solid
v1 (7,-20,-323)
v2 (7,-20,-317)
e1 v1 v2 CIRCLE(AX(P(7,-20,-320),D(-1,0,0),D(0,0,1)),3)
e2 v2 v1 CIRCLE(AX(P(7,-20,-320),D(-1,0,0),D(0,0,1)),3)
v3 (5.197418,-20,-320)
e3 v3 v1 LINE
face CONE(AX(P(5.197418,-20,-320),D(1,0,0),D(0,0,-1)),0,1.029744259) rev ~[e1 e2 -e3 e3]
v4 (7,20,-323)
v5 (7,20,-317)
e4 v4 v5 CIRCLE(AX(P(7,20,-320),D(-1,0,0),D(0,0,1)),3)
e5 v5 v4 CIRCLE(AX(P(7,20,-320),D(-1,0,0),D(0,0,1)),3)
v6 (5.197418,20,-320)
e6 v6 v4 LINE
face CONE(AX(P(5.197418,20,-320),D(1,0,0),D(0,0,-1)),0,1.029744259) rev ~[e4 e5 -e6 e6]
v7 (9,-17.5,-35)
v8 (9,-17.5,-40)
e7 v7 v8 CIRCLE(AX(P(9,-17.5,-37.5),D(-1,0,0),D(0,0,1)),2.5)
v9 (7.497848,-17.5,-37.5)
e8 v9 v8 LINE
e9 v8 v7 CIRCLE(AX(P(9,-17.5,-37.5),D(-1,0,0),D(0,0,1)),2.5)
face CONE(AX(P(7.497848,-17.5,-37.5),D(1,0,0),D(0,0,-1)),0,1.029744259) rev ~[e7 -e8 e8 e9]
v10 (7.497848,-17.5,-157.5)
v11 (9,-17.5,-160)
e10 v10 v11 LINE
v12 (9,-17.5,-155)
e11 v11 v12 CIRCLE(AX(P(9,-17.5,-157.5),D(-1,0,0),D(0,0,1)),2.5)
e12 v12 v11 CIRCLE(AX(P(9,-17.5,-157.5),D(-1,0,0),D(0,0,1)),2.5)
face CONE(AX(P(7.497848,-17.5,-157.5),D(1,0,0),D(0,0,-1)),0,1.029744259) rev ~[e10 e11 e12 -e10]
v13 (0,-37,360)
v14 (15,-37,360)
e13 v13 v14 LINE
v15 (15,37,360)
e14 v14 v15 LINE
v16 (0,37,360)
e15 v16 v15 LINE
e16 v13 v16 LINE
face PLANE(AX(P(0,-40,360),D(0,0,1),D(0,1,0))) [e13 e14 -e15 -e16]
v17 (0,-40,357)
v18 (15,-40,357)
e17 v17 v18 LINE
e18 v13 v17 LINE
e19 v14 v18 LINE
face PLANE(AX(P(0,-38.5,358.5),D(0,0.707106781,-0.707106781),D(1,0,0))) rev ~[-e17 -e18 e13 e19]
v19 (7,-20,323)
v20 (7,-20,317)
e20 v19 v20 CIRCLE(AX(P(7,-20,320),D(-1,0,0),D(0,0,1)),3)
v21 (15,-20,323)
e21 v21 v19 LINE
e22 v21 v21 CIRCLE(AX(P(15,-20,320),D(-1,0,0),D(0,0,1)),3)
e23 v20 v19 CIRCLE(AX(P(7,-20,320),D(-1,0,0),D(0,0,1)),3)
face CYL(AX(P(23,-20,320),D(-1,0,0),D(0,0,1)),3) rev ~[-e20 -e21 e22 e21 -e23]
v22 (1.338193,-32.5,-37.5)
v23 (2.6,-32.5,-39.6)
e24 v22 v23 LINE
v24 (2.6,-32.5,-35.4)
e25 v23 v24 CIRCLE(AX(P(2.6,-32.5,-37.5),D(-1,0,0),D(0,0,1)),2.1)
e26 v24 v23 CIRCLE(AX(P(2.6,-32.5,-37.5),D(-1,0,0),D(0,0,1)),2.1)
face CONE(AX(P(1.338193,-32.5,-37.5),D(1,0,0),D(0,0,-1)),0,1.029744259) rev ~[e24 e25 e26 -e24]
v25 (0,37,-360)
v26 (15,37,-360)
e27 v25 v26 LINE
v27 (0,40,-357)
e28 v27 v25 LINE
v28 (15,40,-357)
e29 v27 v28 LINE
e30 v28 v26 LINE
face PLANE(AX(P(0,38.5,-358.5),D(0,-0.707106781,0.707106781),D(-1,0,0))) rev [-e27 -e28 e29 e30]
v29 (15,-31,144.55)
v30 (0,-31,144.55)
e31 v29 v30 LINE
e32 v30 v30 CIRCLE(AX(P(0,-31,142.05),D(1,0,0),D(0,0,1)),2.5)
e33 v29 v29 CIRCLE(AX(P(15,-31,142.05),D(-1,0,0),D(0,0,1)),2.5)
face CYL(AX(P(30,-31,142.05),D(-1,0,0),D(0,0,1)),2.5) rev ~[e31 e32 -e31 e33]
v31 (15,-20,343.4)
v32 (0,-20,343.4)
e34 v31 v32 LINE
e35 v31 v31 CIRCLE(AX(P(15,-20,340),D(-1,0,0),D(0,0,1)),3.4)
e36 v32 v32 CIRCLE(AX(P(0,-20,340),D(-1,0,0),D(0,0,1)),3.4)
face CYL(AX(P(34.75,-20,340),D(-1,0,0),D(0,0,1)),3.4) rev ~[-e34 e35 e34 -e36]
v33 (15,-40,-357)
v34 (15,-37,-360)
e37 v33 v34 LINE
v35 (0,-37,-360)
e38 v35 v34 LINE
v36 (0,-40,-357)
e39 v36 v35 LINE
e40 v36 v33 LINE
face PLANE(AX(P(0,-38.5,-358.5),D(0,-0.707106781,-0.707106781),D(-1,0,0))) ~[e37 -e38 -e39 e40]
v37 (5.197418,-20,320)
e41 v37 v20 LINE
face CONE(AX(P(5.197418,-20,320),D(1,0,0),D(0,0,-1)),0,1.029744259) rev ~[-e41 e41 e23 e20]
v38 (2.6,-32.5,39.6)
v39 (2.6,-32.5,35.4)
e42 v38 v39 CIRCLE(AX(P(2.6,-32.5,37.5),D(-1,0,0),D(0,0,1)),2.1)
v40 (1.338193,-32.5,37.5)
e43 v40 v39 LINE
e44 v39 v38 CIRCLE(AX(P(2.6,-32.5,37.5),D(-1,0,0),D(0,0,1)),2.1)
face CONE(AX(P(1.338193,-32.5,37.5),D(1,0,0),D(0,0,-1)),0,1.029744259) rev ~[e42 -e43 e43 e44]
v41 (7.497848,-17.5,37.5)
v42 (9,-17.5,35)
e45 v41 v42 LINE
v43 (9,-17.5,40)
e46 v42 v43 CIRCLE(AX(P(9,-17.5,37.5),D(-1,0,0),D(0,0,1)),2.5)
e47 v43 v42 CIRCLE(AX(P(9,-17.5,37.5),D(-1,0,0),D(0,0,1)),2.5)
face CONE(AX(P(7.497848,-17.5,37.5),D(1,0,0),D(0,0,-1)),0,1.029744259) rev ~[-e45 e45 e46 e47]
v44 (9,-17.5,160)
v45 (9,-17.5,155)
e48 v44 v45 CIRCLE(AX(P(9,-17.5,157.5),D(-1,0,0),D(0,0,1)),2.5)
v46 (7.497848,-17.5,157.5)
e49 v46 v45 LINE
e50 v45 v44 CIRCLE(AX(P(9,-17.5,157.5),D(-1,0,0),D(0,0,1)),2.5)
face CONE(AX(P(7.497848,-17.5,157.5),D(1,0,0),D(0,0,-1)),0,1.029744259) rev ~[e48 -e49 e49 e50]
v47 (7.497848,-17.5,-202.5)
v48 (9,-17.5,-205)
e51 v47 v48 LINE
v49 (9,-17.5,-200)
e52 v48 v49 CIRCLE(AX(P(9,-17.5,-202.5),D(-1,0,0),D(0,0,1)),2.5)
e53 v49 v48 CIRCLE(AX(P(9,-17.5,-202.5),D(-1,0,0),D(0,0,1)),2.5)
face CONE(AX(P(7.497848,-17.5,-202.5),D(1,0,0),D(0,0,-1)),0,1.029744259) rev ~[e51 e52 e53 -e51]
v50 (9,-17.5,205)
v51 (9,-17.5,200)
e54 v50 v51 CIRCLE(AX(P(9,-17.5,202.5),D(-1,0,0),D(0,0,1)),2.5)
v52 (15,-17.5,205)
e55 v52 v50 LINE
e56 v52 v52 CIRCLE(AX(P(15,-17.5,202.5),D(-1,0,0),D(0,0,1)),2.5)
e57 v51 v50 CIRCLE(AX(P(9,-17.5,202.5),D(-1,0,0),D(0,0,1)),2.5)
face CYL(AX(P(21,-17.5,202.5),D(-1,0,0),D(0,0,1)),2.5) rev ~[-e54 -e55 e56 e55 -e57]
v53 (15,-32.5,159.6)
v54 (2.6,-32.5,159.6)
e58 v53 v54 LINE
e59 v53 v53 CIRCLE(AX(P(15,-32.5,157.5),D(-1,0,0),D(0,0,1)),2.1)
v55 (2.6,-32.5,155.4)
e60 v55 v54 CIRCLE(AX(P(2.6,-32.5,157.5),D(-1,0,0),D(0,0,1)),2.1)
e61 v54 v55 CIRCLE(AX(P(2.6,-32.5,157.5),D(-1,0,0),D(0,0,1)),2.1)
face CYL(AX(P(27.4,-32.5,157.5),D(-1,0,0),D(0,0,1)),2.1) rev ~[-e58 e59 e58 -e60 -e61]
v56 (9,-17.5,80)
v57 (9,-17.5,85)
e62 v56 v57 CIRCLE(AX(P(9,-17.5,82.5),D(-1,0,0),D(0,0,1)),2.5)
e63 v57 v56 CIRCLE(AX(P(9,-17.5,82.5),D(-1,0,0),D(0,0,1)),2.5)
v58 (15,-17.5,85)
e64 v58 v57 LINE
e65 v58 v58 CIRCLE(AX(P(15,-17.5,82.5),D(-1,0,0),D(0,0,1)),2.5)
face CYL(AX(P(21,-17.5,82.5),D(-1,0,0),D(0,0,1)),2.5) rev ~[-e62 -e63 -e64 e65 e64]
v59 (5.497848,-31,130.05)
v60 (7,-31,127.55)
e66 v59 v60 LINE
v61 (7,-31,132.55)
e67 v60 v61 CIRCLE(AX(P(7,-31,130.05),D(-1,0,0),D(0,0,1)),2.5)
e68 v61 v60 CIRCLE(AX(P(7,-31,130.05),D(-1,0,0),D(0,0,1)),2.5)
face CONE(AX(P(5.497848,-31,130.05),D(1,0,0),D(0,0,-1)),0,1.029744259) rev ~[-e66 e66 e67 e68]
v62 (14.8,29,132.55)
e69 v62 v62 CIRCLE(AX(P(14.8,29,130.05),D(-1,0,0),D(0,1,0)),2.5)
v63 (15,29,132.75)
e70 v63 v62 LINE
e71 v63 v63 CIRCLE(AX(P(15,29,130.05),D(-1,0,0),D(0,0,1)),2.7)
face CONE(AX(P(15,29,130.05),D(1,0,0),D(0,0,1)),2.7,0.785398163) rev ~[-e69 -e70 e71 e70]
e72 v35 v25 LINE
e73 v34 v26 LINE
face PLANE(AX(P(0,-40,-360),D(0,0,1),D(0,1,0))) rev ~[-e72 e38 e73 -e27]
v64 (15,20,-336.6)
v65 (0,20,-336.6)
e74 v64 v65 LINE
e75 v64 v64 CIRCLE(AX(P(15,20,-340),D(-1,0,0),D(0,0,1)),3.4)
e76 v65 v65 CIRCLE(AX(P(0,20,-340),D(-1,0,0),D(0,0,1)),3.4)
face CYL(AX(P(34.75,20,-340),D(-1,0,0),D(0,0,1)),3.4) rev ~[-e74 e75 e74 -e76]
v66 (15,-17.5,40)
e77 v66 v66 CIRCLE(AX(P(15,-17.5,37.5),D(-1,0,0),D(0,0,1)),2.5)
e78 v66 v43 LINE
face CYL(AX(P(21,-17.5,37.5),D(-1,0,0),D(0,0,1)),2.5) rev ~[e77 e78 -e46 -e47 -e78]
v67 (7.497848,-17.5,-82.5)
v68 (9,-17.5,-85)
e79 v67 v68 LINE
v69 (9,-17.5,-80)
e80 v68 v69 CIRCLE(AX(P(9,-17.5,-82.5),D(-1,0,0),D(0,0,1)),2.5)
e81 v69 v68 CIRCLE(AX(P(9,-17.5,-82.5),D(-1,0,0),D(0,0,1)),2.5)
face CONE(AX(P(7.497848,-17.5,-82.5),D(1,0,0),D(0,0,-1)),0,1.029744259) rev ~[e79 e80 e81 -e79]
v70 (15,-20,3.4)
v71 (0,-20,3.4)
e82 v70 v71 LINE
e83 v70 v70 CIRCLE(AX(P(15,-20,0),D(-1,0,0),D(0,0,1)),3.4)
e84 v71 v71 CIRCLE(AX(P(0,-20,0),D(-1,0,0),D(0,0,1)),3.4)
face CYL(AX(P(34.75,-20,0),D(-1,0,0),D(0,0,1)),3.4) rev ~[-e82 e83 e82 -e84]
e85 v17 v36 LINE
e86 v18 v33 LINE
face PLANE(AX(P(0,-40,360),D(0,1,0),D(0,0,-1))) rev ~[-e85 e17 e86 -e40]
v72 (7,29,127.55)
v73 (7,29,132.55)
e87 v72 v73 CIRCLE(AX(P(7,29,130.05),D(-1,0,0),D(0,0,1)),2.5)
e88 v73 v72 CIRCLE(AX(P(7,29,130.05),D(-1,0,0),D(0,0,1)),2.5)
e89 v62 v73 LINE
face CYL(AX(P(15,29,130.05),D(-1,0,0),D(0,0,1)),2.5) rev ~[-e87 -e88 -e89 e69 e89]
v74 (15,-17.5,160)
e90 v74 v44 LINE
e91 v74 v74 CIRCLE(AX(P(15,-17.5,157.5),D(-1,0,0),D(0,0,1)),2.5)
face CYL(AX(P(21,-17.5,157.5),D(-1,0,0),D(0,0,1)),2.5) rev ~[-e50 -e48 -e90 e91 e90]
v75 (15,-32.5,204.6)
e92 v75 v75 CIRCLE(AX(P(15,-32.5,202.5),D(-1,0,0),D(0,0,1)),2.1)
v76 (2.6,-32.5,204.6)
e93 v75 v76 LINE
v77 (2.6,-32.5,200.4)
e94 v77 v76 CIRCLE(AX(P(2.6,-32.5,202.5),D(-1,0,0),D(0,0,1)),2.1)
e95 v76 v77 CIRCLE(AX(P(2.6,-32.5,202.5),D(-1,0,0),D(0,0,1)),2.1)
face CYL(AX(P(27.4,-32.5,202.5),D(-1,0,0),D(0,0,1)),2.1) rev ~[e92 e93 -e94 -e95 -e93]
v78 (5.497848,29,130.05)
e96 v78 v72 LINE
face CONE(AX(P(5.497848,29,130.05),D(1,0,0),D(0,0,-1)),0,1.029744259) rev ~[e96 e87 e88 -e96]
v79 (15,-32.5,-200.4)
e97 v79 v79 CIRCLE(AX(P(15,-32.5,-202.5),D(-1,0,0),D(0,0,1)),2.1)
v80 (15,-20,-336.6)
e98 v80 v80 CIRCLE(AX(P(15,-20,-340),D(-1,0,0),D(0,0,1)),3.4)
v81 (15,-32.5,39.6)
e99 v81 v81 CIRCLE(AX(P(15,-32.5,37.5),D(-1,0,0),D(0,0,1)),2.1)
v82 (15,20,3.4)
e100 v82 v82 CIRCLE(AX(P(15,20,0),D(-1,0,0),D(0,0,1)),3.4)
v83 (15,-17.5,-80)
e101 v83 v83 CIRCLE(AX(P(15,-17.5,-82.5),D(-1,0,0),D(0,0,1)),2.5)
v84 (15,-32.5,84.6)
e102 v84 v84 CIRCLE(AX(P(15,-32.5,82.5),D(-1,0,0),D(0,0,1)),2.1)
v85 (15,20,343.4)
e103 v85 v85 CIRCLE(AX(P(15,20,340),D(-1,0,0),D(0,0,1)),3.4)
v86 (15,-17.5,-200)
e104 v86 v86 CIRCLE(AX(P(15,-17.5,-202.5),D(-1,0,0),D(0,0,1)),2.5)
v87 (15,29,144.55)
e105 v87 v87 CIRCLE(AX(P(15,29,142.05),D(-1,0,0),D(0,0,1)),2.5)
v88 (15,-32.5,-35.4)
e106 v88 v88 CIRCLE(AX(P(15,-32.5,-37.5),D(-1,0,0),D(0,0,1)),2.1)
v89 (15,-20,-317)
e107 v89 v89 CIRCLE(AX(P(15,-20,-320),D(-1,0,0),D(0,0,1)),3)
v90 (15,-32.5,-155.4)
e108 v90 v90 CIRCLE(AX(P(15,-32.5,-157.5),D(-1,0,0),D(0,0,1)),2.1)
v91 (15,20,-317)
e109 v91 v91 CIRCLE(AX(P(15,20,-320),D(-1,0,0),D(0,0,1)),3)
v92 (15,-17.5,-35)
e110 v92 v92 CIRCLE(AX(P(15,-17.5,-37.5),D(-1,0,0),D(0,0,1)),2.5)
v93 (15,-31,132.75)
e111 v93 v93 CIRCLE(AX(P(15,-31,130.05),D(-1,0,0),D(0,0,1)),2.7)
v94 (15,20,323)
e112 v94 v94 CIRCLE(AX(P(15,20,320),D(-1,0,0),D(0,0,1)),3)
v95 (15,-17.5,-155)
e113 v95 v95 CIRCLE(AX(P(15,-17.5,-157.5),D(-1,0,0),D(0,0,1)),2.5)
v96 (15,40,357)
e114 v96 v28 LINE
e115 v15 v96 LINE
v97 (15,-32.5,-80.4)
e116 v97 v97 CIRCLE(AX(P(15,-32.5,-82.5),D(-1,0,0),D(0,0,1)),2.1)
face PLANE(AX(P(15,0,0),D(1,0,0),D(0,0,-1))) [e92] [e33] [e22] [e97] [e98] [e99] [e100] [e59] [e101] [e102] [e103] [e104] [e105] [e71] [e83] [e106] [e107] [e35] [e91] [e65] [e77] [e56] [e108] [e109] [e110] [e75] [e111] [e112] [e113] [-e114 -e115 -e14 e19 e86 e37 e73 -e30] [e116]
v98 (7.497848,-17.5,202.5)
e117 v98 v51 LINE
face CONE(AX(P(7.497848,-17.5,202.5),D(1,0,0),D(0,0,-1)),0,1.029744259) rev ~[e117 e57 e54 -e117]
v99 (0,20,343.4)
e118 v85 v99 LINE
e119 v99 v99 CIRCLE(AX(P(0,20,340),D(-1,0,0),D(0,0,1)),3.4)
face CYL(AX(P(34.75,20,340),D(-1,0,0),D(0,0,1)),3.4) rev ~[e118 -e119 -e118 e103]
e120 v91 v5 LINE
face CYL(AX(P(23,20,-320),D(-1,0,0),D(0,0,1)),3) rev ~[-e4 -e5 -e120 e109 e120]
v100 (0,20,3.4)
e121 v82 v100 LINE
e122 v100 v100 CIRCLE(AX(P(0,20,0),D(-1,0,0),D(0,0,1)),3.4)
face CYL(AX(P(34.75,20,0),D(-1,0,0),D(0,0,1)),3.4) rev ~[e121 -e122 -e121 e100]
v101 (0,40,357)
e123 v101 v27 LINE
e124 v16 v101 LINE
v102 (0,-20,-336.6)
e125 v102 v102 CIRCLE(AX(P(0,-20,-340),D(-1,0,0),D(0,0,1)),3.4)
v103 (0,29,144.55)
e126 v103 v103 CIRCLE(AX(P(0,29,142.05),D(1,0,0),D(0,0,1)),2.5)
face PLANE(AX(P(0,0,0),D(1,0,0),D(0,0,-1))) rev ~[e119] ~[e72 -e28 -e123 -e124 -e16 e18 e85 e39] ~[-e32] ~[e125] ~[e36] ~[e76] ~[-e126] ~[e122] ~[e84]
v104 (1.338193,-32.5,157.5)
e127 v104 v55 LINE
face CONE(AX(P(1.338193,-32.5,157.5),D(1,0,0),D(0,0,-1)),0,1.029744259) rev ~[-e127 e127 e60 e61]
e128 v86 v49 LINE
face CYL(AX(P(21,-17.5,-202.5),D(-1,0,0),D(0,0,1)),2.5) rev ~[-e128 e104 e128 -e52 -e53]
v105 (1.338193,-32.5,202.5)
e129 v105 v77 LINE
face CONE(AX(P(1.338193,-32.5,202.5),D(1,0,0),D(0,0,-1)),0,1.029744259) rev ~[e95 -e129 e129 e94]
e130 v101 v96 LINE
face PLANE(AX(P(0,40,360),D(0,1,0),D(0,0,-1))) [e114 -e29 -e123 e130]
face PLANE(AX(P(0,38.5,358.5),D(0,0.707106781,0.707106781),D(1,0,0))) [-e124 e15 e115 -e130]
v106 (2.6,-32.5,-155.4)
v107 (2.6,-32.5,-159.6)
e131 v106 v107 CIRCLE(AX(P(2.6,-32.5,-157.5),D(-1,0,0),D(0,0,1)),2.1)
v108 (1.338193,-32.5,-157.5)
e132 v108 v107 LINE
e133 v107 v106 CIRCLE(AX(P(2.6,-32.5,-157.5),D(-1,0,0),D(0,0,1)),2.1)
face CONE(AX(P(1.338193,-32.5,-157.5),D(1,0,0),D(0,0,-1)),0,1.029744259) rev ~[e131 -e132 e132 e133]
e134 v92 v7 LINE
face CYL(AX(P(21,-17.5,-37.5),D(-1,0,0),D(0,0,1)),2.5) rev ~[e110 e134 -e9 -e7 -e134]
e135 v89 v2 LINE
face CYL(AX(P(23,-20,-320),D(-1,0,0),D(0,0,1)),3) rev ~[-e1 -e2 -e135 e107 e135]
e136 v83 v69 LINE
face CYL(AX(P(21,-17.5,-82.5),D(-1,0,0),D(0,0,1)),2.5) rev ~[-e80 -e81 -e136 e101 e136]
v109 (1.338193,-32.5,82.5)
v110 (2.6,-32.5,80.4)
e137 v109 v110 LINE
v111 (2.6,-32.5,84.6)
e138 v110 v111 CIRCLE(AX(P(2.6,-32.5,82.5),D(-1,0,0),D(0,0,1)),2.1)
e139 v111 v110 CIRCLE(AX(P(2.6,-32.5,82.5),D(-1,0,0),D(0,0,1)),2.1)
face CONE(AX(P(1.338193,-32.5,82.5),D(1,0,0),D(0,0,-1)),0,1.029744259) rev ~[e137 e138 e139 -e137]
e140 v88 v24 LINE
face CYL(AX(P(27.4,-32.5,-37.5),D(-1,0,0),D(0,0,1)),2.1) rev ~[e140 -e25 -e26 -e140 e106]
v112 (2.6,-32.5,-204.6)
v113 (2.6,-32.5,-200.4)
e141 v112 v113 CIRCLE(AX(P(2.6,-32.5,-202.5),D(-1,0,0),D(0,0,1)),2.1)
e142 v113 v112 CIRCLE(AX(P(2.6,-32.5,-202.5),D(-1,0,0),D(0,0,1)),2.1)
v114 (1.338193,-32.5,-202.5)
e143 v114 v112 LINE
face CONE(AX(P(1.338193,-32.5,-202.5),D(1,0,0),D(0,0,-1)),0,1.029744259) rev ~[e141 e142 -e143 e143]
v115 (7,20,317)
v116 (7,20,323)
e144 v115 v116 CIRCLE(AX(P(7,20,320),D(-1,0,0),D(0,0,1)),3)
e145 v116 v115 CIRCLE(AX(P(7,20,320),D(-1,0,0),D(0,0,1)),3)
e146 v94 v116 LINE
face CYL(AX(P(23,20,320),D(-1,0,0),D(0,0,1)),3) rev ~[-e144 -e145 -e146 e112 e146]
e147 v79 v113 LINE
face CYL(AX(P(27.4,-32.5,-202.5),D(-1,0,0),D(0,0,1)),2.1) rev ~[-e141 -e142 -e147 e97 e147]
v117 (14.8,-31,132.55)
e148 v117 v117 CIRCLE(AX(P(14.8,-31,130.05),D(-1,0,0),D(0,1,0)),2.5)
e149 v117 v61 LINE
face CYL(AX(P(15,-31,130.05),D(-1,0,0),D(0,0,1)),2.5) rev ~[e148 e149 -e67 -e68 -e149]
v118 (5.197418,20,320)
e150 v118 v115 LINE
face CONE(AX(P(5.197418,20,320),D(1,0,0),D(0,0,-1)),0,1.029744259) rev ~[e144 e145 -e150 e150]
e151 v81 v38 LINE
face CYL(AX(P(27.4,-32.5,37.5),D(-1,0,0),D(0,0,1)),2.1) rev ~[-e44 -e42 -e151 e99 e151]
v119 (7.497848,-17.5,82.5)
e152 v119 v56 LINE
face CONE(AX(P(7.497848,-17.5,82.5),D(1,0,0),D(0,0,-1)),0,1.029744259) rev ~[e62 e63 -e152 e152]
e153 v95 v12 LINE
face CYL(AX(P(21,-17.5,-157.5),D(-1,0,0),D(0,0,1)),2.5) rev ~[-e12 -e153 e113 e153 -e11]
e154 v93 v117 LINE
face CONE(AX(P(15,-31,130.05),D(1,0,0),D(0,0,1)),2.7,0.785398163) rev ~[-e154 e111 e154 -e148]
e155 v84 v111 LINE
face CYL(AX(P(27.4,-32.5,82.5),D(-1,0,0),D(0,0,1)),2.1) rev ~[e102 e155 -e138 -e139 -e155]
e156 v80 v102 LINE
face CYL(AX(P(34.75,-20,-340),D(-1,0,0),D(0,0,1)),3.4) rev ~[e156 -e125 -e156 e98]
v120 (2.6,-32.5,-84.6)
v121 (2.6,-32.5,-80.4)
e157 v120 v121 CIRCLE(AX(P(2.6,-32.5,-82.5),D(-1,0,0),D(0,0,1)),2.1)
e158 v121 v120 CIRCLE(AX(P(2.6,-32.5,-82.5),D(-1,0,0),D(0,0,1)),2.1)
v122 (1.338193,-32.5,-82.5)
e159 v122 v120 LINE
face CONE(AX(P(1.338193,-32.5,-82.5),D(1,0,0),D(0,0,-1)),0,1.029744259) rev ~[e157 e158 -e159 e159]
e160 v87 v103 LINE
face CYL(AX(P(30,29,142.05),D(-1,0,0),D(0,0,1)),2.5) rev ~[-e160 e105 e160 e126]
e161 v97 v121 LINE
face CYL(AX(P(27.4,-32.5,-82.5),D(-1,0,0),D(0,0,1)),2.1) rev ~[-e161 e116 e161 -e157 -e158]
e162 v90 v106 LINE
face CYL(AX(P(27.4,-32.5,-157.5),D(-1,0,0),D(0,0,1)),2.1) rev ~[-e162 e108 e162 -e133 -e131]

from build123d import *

# Parameters (mm, degrees)
SKETCH1_W                        = 720
SKETCH1_H                        = 80
BOSS_EXTRUDE1_DEPTH              = 15
M5_TAPPED_HOLE1_D                = 4.2
M5_TAPPED_HOLE1_DEPTH            = 12.4
M5_TAPPED_HOLE1_TIP              = 1.2618073
F_5_0MM_BLIND_HOLE_1_D           = 5
F_5_0MM_BLIND_HOLE_1_DEPTH       = 6
F_5_0MM_BLIND_HOLE_1_TIP         = 1.502151548
M8_TAPPED_HOLE1_D                = 6.8
M8_TAPPED_HOLE1_DEPTH            = 19.75
M8_TAPPED_HOLE1_TIP              = 2.042926105
F_6_0MM_BLIND_HOLE_1_D           = 6
F_6_0MM_BLIND_HOLE_1_DEPTH       = 8
F_6_0MM_BLIND_HOLE_1_TIP         = 1.802581857
M8_TAPPED_HOLE2_D                = 6.8
M8_TAPPED_HOLE2_DEPTH            = 19.75
M8_TAPPED_HOLE2_TIP              = 2.042926105
M6_TAPPED_HOLE1_D                = 5
M6_TAPPED_HOLE1_DEPTH            = 15
M6_TAPPED_HOLE1_TIP              = 1.502151548
F_5_0MM_BLIND_HOLE_2_D           = 5
F_5_0MM_BLIND_HOLE_2_DEPTH       = 8
F_5_0MM_BLIND_HOLE_2_CSINK_D     = 5.4
F_5_0MM_BLIND_HOLE_2_CSINK_ANGLE = 90
F_5_0MM_BLIND_HOLE_2_TIP         = 1.502151548
CHAMFER1_SIZE                    = 3


with BuildPart() as part:
    # Sketch1 → Boss-Extrude1 (new body)
    with BuildSketch(Plane(origin=(0, 0, 0), x_dir=(0, 0, -1), z_dir=(1, 0, 0))):
        Rectangle(SKETCH1_W, SKETCH1_H)
    extrude(amount=BOSS_EXTRUDE1_DEPTH)

    # M5 Tapped Hole1
    with Locations(Plane(origin=(15, 0, 0), x_dir=(0, 0, -1), z_dir=(1, 0, 0))):
        with Locations((202.5, -32.5), (157.5, -32.5), (82.5, -32.5), (37.5, -32.5), (-37.5, -32.5), (-82.5, -32.5), (-157.5, -32.5), (-202.5, -32.5)):
            Hole(M5_TAPPED_HOLE1_D / 2, depth=M5_TAPPED_HOLE1_DEPTH)
            with Locations((0, 0, -(M5_TAPPED_HOLE1_DEPTH + M5_TAPPED_HOLE1_TIP / 2))):  # 118° drill point
                Cone(0, M5_TAPPED_HOLE1_D / 2, M5_TAPPED_HOLE1_TIP, mode=Mode.SUBTRACT)

    # Ø5.0mm blind hole 1
    with Locations(Plane(origin=(15, 0, 0), x_dir=(0, 0, -1), z_dir=(1, 0, 0))):
        with Locations((-202.5, -17.5), (-157.5, -17.5), (-82.5, -17.5), (-37.5, -17.5), (37.5, -17.5), (82.5, -17.5), (157.5, -17.5), (202.5, -17.5)):
            Hole(F_5_0MM_BLIND_HOLE_1_D / 2, depth=F_5_0MM_BLIND_HOLE_1_DEPTH)
            with Locations((0, 0, -(F_5_0MM_BLIND_HOLE_1_DEPTH + F_5_0MM_BLIND_HOLE_1_TIP / 2))):  # 118° drill point
                Cone(0, F_5_0MM_BLIND_HOLE_1_D / 2, F_5_0MM_BLIND_HOLE_1_TIP, mode=Mode.SUBTRACT)

    # M8 Tapped Hole1
    with Locations(Plane(origin=(15, 0, 0), x_dir=(0, 0, -1), z_dir=(1, 0, 0))):
        with Locations((340, 20), (-340, 20), (-340, -20), (340, -20)):
            Hole(M8_TAPPED_HOLE1_D / 2, depth=M8_TAPPED_HOLE1_DEPTH)
            with Locations((0, 0, -(M8_TAPPED_HOLE1_DEPTH + M8_TAPPED_HOLE1_TIP / 2))):  # 118° drill point
                Cone(0, M8_TAPPED_HOLE1_D / 2, M8_TAPPED_HOLE1_TIP, mode=Mode.SUBTRACT)

    # Ø6.0mm blind hole 1
    with Locations(Plane(origin=(15, 0, 0), x_dir=(0, 0, -1), z_dir=(1, 0, 0))):
        with Locations((320, -20), (-320, 20), (-320, -20), (320, 20)):
            Hole(F_6_0MM_BLIND_HOLE_1_D / 2, depth=F_6_0MM_BLIND_HOLE_1_DEPTH)
            with Locations((0, 0, -(F_6_0MM_BLIND_HOLE_1_DEPTH + F_6_0MM_BLIND_HOLE_1_TIP / 2))):  # 118° drill point
                Cone(0, F_6_0MM_BLIND_HOLE_1_D / 2, F_6_0MM_BLIND_HOLE_1_TIP, mode=Mode.SUBTRACT)

    # M8 Tapped Hole2
    with Locations(Plane(origin=(15, 0, 0), x_dir=(0, 0, -1), z_dir=(1, 0, 0))):
        with Locations((0, -20), (0, 20)):
            Hole(M8_TAPPED_HOLE2_D / 2, depth=M8_TAPPED_HOLE2_DEPTH)
            with Locations((0, 0, -(M8_TAPPED_HOLE2_DEPTH + M8_TAPPED_HOLE2_TIP / 2))):  # 118° drill point
                Cone(0, M8_TAPPED_HOLE2_D / 2, M8_TAPPED_HOLE2_TIP, mode=Mode.SUBTRACT)

    # M6 Tapped Hole1
    with Locations(Plane(origin=(15, 0, 0), x_dir=(0, 0, -1), z_dir=(1, 0, 0))):
        with Locations((-142.05, 29), (-142.05, -31)):
            Hole(M6_TAPPED_HOLE1_D / 2, depth=M6_TAPPED_HOLE1_DEPTH)
            with Locations((0, 0, -(M6_TAPPED_HOLE1_DEPTH + M6_TAPPED_HOLE1_TIP / 2))):  # 118° drill point
                Cone(0, M6_TAPPED_HOLE1_D / 2, M6_TAPPED_HOLE1_TIP, mode=Mode.SUBTRACT)

    # Ø5.0mm blind hole 2
    with Locations(Plane(origin=(15, 0, 0), x_dir=(0, 0, -1), z_dir=(1, 0, 0))):
        with Locations((-130.05, -31), (-130.05, 29)):
            CounterSinkHole(F_5_0MM_BLIND_HOLE_2_D / 2, F_5_0MM_BLIND_HOLE_2_CSINK_D / 2, depth=F_5_0MM_BLIND_HOLE_2_DEPTH, counter_sink_angle=F_5_0MM_BLIND_HOLE_2_CSINK_ANGLE)
            with Locations((0, 0, -(F_5_0MM_BLIND_HOLE_2_DEPTH + F_5_0MM_BLIND_HOLE_2_TIP / 2))):  # 118° drill point
                Cone(0, F_5_0MM_BLIND_HOLE_2_D / 2, F_5_0MM_BLIND_HOLE_2_TIP, mode=Mode.SUBTRACT)

    # Chamfer1
    chamfer1_edges = [part.edges().sort_by_distance(p)[0] for p in [
        (7.5, -40, -360),
        (7.5, -40, 360),
        (7.5, 40, 360),
        (7.5, 40, -360),
    ]]
    chamfer(chamfer1_edges, length=CHAMFER1_SIZE)


solid = part.part
